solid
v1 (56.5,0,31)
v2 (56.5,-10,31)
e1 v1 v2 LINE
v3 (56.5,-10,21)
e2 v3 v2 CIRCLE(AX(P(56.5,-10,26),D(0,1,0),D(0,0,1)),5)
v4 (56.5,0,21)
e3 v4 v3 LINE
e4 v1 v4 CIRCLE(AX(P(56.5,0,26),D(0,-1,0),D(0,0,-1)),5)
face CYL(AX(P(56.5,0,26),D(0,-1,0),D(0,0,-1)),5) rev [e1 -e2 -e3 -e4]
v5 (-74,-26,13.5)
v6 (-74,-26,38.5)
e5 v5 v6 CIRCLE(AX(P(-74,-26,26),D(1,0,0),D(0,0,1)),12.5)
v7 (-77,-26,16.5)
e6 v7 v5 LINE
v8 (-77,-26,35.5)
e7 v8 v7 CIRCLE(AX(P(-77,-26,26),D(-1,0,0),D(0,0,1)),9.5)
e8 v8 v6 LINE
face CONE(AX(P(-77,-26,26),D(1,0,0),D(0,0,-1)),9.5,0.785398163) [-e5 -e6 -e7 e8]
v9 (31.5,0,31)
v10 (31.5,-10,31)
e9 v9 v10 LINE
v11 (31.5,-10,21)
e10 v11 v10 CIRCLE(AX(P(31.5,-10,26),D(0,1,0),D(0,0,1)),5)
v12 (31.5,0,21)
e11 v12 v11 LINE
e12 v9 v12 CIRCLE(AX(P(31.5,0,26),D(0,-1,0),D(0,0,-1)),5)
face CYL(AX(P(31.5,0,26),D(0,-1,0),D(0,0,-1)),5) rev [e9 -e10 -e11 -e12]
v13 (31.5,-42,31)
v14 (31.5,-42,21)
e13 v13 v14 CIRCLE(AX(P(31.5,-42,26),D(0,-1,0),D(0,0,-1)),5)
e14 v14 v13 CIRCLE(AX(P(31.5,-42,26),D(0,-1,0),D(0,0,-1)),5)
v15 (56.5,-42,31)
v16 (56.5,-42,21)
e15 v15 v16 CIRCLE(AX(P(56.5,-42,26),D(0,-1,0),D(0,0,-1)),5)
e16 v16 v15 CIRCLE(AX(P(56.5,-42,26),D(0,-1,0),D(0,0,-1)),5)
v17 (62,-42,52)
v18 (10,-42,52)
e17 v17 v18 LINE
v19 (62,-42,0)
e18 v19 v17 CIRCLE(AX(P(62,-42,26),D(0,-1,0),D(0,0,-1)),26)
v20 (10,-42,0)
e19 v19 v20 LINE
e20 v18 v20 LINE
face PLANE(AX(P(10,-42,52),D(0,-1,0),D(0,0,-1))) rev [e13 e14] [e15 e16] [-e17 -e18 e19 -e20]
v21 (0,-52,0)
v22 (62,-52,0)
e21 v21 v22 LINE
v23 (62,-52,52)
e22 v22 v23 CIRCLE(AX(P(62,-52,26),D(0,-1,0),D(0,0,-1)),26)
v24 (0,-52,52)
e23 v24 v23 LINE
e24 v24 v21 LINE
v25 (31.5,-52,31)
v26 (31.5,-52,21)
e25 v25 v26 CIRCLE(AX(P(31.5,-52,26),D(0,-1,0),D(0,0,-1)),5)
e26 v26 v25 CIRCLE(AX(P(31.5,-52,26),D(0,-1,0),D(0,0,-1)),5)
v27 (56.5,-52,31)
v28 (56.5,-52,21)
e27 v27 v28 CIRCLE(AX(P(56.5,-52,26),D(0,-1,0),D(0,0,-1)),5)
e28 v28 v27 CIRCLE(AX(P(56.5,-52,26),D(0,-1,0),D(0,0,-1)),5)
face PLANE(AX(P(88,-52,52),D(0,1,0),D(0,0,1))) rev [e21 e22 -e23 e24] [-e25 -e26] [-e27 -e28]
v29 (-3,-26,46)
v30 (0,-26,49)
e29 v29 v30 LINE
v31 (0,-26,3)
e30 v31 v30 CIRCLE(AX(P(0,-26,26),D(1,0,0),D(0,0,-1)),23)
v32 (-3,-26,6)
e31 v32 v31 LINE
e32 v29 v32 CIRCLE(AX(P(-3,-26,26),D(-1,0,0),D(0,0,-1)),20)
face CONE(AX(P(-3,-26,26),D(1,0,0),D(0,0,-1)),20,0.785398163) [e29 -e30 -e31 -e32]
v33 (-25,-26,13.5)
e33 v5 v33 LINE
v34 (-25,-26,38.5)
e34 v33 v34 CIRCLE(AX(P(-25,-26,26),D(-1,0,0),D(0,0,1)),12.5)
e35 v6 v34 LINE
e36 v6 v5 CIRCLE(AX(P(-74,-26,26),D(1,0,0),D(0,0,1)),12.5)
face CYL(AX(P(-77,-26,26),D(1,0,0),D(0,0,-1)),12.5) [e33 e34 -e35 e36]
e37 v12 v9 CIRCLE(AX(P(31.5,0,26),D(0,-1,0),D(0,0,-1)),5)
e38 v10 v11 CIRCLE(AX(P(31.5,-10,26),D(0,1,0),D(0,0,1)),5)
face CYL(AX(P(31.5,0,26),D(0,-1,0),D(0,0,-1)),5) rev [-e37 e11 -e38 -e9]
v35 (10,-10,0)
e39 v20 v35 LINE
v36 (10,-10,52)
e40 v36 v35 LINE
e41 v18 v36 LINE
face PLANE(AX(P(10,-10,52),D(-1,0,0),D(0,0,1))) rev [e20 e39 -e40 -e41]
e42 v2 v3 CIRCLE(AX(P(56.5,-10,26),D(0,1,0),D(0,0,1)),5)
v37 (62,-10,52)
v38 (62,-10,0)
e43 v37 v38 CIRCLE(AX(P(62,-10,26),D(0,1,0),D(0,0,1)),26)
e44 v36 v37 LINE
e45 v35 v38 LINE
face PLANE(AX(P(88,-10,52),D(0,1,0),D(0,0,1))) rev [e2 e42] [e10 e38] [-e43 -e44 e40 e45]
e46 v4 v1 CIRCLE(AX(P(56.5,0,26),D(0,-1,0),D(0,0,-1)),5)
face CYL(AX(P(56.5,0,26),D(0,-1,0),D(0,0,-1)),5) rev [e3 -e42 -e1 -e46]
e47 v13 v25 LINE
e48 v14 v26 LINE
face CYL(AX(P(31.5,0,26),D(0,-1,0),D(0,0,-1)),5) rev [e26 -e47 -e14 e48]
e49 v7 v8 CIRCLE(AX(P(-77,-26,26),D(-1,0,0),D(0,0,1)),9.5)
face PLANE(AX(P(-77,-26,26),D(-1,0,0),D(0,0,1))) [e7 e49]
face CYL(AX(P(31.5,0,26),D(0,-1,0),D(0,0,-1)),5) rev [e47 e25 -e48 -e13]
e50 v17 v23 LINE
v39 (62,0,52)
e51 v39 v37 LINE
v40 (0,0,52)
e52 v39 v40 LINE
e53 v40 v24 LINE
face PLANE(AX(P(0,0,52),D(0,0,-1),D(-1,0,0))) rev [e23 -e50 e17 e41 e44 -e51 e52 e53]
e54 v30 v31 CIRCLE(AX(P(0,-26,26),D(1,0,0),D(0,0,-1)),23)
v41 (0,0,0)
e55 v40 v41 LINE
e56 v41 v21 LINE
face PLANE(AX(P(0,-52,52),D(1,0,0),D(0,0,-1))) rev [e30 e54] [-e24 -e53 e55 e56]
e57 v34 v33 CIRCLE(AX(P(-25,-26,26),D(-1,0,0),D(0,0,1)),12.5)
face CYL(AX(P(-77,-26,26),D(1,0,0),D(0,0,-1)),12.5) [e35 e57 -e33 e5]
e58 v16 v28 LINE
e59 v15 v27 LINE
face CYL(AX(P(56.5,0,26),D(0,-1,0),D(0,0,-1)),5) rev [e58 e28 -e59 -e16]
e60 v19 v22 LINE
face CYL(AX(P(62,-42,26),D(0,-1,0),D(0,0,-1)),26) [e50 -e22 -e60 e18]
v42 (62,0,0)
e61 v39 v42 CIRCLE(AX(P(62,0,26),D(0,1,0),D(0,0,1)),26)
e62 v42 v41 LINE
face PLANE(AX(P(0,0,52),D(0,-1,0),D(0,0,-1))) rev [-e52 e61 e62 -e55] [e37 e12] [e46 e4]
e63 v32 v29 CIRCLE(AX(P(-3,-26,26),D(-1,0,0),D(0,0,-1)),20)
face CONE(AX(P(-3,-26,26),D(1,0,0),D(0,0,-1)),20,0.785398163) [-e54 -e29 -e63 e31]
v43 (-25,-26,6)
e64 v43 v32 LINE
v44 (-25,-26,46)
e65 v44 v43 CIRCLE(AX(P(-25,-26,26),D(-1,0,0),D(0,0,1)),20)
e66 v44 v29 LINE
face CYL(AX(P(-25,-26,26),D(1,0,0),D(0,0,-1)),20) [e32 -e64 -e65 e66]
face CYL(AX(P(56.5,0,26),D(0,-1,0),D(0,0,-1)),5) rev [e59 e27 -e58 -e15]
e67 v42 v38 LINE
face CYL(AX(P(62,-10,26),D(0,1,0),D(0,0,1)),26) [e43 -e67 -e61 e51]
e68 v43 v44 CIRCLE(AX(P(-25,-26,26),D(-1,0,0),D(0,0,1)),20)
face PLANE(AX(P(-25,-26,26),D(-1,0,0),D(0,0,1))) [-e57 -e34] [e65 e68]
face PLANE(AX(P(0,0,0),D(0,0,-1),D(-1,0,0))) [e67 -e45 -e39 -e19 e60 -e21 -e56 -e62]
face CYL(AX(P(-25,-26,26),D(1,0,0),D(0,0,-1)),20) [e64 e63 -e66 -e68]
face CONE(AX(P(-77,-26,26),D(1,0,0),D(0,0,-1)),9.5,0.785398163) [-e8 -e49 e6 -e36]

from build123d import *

# Parameters (mm, degrees)
CLEVIS_BODY_52MM_DEPTH          = 52
ARM_END_BOSS_1_DEPTH            = 10
ARM_START                       = -10
ARM_END_BOSS_2_DEPTH            = 10
FORK_START                      = -70
FORK_TRIM_CUT_DEPTH             = 70
FORK_SLOT_PROFILE_W             = 26
FORK_SLOT_PROFILE_H             = 52
FORK_SLOT_CUT_DEPTH             = 70
ARM_END_BOSS_3_DEPTH            = 10
ARM_END_BOSS_4_DEPTH            = 10
COLLAR_PROFILE_R                = 20
COLLAR_25MM_DEPTH               = 25
COLLAR_CHAMFER_3X45_SIZE        = 3
SHANK_PROFILE_R                 = 12.5
SHANK_52MM_DEPTH                = 52
SHANK_END_CHAMFER_3X45_SIZE     = 3
PIN_HOLES_PROFILE_R             = 5
PIN_HOLES_2X_THROUGH_ARMS_DEPTH = 52


with BuildPart() as part:
    # Clevis Body Profile → Clevis Body 52mm (new body)
    with BuildSketch(Plane.XY):
        Polygon((0, 0), (88, 0), (88, -10), (10, -10), (10, -42), (88, -42), (88, -52), (0, -52), align=None)
    extrude(amount=CLEVIS_BODY_52MM_DEPTH)

    # Arm End Boss 1 Profile → Arm End Boss 1 (add)
    with BuildSketch(Plane(origin=(0, 0, 0), x_dir=(1, 0, 0), z_dir=(0, 1, 0))):
        with BuildLine():
            Line((88, 0), (88, -52))
            ThreePointArc((88, -52), (114, -26), (88, 0))
        make_face()
    extrude(amount=-ARM_END_BOSS_1_DEPTH)

    # Arm End Boss 2 Profile → Arm End Boss 2 (add)
    with BuildSketch(Plane.XZ.offset(52).offset(ARM_START)):
        with BuildLine():
            Line((88, 52), (88, 0))
            ThreePointArc((88, 0), (114, 26), (88, 52))
        make_face()
    extrude(amount=ARM_END_BOSS_2_DEPTH)

    # Fork Trim Cut Profile → Fork Trim Cut (cut)
    with BuildSketch(Plane.XZ.offset(52).offset(FORK_START)):
        with BuildLine():
            Line((88, 52), (88, 0))
            ThreePointArc((88, 0), (114, 26), (88, 52))
        make_face()
    extrude(amount=FORK_TRIM_CUT_DEPTH, mode=Mode.SUBTRACT)

    # Fork Slot Profile → Fork Slot Cut (cut)
    with BuildSketch(Plane.XZ.offset(52)):
        with Locations((75, 26)):
            Rectangle(FORK_SLOT_PROFILE_W, FORK_SLOT_PROFILE_H)
    extrude(amount=-FORK_SLOT_CUT_DEPTH, mode=Mode.SUBTRACT)

    # Arm End Boss 3 Profile → Arm End Boss 3 (add)
    with BuildSketch(Plane.XZ.offset(52)):
        with BuildLine():
            Line((62, 52), (62, 0))
            ThreePointArc((62, 0), (88, 26), (62, 52))
        make_face()
    extrude(amount=-ARM_END_BOSS_3_DEPTH)

    # Arm End Boss 4 Profile → Arm End Boss 4 (add)
    with BuildSketch(Plane(origin=(0, 0, 0), x_dir=(1, 0, 0), z_dir=(0, 1, 0)).offset(ARM_START)):
        with BuildLine():
            Line((62, 0), (62, -52))
            ThreePointArc((62, -52), (88, -26), (62, 0))
        make_face()
    extrude(amount=ARM_END_BOSS_4_DEPTH)

    # Collar Profile → Collar 25mm (add)
    with BuildSketch(Plane.ZY):
        with Locations((26, -26)):
            Circle(COLLAR_PROFILE_R)
    extrude(amount=COLLAR_25MM_DEPTH)

    # Collar Chamfer 3x45
    collar_chamfer_3x45_edges = [part.edges().sort_by_distance(p)[0] for p in [
        (0, -26, 6),
    ]]
    chamfer(collar_chamfer_3x45_edges, length=COLLAR_CHAMFER_3X45_SIZE)

    # Shank Profile → Shank 52mm (add)
    with BuildSketch(Plane.ZY.offset(25)):
        with Locations(Location((26, -26, 0), (0, 0, 180))):
            Circle(SHANK_PROFILE_R)
    extrude(amount=SHANK_52MM_DEPTH)

    # Shank End Chamfer 3x45
    shank_end_chamfer_3x45_edges = [part.edges().sort_by_distance(p)[0] for p in [
        (-77, -26, 38.5),
    ]]
    chamfer(shank_end_chamfer_3x45_edges, length=SHANK_END_CHAMFER_3X45_SIZE)

    # Pin Holes Profile → Pin Holes 2x Through Arms (cut)
    with BuildSketch(Plane.XZ.offset(52)):
        with Locations(Location((31.5, 26, 0), (0, 0, 270))):
            Circle(PIN_HOLES_PROFILE_R)
        with Locations(Location((56.5, 26, 0), (0, 0, 270))):
            Circle(PIN_HOLES_PROFILE_R)
    extrude(amount=-PIN_HOLES_2X_THROUGH_ARMS_DEPTH, mode=Mode.SUBTRACT)


solid = part.part
